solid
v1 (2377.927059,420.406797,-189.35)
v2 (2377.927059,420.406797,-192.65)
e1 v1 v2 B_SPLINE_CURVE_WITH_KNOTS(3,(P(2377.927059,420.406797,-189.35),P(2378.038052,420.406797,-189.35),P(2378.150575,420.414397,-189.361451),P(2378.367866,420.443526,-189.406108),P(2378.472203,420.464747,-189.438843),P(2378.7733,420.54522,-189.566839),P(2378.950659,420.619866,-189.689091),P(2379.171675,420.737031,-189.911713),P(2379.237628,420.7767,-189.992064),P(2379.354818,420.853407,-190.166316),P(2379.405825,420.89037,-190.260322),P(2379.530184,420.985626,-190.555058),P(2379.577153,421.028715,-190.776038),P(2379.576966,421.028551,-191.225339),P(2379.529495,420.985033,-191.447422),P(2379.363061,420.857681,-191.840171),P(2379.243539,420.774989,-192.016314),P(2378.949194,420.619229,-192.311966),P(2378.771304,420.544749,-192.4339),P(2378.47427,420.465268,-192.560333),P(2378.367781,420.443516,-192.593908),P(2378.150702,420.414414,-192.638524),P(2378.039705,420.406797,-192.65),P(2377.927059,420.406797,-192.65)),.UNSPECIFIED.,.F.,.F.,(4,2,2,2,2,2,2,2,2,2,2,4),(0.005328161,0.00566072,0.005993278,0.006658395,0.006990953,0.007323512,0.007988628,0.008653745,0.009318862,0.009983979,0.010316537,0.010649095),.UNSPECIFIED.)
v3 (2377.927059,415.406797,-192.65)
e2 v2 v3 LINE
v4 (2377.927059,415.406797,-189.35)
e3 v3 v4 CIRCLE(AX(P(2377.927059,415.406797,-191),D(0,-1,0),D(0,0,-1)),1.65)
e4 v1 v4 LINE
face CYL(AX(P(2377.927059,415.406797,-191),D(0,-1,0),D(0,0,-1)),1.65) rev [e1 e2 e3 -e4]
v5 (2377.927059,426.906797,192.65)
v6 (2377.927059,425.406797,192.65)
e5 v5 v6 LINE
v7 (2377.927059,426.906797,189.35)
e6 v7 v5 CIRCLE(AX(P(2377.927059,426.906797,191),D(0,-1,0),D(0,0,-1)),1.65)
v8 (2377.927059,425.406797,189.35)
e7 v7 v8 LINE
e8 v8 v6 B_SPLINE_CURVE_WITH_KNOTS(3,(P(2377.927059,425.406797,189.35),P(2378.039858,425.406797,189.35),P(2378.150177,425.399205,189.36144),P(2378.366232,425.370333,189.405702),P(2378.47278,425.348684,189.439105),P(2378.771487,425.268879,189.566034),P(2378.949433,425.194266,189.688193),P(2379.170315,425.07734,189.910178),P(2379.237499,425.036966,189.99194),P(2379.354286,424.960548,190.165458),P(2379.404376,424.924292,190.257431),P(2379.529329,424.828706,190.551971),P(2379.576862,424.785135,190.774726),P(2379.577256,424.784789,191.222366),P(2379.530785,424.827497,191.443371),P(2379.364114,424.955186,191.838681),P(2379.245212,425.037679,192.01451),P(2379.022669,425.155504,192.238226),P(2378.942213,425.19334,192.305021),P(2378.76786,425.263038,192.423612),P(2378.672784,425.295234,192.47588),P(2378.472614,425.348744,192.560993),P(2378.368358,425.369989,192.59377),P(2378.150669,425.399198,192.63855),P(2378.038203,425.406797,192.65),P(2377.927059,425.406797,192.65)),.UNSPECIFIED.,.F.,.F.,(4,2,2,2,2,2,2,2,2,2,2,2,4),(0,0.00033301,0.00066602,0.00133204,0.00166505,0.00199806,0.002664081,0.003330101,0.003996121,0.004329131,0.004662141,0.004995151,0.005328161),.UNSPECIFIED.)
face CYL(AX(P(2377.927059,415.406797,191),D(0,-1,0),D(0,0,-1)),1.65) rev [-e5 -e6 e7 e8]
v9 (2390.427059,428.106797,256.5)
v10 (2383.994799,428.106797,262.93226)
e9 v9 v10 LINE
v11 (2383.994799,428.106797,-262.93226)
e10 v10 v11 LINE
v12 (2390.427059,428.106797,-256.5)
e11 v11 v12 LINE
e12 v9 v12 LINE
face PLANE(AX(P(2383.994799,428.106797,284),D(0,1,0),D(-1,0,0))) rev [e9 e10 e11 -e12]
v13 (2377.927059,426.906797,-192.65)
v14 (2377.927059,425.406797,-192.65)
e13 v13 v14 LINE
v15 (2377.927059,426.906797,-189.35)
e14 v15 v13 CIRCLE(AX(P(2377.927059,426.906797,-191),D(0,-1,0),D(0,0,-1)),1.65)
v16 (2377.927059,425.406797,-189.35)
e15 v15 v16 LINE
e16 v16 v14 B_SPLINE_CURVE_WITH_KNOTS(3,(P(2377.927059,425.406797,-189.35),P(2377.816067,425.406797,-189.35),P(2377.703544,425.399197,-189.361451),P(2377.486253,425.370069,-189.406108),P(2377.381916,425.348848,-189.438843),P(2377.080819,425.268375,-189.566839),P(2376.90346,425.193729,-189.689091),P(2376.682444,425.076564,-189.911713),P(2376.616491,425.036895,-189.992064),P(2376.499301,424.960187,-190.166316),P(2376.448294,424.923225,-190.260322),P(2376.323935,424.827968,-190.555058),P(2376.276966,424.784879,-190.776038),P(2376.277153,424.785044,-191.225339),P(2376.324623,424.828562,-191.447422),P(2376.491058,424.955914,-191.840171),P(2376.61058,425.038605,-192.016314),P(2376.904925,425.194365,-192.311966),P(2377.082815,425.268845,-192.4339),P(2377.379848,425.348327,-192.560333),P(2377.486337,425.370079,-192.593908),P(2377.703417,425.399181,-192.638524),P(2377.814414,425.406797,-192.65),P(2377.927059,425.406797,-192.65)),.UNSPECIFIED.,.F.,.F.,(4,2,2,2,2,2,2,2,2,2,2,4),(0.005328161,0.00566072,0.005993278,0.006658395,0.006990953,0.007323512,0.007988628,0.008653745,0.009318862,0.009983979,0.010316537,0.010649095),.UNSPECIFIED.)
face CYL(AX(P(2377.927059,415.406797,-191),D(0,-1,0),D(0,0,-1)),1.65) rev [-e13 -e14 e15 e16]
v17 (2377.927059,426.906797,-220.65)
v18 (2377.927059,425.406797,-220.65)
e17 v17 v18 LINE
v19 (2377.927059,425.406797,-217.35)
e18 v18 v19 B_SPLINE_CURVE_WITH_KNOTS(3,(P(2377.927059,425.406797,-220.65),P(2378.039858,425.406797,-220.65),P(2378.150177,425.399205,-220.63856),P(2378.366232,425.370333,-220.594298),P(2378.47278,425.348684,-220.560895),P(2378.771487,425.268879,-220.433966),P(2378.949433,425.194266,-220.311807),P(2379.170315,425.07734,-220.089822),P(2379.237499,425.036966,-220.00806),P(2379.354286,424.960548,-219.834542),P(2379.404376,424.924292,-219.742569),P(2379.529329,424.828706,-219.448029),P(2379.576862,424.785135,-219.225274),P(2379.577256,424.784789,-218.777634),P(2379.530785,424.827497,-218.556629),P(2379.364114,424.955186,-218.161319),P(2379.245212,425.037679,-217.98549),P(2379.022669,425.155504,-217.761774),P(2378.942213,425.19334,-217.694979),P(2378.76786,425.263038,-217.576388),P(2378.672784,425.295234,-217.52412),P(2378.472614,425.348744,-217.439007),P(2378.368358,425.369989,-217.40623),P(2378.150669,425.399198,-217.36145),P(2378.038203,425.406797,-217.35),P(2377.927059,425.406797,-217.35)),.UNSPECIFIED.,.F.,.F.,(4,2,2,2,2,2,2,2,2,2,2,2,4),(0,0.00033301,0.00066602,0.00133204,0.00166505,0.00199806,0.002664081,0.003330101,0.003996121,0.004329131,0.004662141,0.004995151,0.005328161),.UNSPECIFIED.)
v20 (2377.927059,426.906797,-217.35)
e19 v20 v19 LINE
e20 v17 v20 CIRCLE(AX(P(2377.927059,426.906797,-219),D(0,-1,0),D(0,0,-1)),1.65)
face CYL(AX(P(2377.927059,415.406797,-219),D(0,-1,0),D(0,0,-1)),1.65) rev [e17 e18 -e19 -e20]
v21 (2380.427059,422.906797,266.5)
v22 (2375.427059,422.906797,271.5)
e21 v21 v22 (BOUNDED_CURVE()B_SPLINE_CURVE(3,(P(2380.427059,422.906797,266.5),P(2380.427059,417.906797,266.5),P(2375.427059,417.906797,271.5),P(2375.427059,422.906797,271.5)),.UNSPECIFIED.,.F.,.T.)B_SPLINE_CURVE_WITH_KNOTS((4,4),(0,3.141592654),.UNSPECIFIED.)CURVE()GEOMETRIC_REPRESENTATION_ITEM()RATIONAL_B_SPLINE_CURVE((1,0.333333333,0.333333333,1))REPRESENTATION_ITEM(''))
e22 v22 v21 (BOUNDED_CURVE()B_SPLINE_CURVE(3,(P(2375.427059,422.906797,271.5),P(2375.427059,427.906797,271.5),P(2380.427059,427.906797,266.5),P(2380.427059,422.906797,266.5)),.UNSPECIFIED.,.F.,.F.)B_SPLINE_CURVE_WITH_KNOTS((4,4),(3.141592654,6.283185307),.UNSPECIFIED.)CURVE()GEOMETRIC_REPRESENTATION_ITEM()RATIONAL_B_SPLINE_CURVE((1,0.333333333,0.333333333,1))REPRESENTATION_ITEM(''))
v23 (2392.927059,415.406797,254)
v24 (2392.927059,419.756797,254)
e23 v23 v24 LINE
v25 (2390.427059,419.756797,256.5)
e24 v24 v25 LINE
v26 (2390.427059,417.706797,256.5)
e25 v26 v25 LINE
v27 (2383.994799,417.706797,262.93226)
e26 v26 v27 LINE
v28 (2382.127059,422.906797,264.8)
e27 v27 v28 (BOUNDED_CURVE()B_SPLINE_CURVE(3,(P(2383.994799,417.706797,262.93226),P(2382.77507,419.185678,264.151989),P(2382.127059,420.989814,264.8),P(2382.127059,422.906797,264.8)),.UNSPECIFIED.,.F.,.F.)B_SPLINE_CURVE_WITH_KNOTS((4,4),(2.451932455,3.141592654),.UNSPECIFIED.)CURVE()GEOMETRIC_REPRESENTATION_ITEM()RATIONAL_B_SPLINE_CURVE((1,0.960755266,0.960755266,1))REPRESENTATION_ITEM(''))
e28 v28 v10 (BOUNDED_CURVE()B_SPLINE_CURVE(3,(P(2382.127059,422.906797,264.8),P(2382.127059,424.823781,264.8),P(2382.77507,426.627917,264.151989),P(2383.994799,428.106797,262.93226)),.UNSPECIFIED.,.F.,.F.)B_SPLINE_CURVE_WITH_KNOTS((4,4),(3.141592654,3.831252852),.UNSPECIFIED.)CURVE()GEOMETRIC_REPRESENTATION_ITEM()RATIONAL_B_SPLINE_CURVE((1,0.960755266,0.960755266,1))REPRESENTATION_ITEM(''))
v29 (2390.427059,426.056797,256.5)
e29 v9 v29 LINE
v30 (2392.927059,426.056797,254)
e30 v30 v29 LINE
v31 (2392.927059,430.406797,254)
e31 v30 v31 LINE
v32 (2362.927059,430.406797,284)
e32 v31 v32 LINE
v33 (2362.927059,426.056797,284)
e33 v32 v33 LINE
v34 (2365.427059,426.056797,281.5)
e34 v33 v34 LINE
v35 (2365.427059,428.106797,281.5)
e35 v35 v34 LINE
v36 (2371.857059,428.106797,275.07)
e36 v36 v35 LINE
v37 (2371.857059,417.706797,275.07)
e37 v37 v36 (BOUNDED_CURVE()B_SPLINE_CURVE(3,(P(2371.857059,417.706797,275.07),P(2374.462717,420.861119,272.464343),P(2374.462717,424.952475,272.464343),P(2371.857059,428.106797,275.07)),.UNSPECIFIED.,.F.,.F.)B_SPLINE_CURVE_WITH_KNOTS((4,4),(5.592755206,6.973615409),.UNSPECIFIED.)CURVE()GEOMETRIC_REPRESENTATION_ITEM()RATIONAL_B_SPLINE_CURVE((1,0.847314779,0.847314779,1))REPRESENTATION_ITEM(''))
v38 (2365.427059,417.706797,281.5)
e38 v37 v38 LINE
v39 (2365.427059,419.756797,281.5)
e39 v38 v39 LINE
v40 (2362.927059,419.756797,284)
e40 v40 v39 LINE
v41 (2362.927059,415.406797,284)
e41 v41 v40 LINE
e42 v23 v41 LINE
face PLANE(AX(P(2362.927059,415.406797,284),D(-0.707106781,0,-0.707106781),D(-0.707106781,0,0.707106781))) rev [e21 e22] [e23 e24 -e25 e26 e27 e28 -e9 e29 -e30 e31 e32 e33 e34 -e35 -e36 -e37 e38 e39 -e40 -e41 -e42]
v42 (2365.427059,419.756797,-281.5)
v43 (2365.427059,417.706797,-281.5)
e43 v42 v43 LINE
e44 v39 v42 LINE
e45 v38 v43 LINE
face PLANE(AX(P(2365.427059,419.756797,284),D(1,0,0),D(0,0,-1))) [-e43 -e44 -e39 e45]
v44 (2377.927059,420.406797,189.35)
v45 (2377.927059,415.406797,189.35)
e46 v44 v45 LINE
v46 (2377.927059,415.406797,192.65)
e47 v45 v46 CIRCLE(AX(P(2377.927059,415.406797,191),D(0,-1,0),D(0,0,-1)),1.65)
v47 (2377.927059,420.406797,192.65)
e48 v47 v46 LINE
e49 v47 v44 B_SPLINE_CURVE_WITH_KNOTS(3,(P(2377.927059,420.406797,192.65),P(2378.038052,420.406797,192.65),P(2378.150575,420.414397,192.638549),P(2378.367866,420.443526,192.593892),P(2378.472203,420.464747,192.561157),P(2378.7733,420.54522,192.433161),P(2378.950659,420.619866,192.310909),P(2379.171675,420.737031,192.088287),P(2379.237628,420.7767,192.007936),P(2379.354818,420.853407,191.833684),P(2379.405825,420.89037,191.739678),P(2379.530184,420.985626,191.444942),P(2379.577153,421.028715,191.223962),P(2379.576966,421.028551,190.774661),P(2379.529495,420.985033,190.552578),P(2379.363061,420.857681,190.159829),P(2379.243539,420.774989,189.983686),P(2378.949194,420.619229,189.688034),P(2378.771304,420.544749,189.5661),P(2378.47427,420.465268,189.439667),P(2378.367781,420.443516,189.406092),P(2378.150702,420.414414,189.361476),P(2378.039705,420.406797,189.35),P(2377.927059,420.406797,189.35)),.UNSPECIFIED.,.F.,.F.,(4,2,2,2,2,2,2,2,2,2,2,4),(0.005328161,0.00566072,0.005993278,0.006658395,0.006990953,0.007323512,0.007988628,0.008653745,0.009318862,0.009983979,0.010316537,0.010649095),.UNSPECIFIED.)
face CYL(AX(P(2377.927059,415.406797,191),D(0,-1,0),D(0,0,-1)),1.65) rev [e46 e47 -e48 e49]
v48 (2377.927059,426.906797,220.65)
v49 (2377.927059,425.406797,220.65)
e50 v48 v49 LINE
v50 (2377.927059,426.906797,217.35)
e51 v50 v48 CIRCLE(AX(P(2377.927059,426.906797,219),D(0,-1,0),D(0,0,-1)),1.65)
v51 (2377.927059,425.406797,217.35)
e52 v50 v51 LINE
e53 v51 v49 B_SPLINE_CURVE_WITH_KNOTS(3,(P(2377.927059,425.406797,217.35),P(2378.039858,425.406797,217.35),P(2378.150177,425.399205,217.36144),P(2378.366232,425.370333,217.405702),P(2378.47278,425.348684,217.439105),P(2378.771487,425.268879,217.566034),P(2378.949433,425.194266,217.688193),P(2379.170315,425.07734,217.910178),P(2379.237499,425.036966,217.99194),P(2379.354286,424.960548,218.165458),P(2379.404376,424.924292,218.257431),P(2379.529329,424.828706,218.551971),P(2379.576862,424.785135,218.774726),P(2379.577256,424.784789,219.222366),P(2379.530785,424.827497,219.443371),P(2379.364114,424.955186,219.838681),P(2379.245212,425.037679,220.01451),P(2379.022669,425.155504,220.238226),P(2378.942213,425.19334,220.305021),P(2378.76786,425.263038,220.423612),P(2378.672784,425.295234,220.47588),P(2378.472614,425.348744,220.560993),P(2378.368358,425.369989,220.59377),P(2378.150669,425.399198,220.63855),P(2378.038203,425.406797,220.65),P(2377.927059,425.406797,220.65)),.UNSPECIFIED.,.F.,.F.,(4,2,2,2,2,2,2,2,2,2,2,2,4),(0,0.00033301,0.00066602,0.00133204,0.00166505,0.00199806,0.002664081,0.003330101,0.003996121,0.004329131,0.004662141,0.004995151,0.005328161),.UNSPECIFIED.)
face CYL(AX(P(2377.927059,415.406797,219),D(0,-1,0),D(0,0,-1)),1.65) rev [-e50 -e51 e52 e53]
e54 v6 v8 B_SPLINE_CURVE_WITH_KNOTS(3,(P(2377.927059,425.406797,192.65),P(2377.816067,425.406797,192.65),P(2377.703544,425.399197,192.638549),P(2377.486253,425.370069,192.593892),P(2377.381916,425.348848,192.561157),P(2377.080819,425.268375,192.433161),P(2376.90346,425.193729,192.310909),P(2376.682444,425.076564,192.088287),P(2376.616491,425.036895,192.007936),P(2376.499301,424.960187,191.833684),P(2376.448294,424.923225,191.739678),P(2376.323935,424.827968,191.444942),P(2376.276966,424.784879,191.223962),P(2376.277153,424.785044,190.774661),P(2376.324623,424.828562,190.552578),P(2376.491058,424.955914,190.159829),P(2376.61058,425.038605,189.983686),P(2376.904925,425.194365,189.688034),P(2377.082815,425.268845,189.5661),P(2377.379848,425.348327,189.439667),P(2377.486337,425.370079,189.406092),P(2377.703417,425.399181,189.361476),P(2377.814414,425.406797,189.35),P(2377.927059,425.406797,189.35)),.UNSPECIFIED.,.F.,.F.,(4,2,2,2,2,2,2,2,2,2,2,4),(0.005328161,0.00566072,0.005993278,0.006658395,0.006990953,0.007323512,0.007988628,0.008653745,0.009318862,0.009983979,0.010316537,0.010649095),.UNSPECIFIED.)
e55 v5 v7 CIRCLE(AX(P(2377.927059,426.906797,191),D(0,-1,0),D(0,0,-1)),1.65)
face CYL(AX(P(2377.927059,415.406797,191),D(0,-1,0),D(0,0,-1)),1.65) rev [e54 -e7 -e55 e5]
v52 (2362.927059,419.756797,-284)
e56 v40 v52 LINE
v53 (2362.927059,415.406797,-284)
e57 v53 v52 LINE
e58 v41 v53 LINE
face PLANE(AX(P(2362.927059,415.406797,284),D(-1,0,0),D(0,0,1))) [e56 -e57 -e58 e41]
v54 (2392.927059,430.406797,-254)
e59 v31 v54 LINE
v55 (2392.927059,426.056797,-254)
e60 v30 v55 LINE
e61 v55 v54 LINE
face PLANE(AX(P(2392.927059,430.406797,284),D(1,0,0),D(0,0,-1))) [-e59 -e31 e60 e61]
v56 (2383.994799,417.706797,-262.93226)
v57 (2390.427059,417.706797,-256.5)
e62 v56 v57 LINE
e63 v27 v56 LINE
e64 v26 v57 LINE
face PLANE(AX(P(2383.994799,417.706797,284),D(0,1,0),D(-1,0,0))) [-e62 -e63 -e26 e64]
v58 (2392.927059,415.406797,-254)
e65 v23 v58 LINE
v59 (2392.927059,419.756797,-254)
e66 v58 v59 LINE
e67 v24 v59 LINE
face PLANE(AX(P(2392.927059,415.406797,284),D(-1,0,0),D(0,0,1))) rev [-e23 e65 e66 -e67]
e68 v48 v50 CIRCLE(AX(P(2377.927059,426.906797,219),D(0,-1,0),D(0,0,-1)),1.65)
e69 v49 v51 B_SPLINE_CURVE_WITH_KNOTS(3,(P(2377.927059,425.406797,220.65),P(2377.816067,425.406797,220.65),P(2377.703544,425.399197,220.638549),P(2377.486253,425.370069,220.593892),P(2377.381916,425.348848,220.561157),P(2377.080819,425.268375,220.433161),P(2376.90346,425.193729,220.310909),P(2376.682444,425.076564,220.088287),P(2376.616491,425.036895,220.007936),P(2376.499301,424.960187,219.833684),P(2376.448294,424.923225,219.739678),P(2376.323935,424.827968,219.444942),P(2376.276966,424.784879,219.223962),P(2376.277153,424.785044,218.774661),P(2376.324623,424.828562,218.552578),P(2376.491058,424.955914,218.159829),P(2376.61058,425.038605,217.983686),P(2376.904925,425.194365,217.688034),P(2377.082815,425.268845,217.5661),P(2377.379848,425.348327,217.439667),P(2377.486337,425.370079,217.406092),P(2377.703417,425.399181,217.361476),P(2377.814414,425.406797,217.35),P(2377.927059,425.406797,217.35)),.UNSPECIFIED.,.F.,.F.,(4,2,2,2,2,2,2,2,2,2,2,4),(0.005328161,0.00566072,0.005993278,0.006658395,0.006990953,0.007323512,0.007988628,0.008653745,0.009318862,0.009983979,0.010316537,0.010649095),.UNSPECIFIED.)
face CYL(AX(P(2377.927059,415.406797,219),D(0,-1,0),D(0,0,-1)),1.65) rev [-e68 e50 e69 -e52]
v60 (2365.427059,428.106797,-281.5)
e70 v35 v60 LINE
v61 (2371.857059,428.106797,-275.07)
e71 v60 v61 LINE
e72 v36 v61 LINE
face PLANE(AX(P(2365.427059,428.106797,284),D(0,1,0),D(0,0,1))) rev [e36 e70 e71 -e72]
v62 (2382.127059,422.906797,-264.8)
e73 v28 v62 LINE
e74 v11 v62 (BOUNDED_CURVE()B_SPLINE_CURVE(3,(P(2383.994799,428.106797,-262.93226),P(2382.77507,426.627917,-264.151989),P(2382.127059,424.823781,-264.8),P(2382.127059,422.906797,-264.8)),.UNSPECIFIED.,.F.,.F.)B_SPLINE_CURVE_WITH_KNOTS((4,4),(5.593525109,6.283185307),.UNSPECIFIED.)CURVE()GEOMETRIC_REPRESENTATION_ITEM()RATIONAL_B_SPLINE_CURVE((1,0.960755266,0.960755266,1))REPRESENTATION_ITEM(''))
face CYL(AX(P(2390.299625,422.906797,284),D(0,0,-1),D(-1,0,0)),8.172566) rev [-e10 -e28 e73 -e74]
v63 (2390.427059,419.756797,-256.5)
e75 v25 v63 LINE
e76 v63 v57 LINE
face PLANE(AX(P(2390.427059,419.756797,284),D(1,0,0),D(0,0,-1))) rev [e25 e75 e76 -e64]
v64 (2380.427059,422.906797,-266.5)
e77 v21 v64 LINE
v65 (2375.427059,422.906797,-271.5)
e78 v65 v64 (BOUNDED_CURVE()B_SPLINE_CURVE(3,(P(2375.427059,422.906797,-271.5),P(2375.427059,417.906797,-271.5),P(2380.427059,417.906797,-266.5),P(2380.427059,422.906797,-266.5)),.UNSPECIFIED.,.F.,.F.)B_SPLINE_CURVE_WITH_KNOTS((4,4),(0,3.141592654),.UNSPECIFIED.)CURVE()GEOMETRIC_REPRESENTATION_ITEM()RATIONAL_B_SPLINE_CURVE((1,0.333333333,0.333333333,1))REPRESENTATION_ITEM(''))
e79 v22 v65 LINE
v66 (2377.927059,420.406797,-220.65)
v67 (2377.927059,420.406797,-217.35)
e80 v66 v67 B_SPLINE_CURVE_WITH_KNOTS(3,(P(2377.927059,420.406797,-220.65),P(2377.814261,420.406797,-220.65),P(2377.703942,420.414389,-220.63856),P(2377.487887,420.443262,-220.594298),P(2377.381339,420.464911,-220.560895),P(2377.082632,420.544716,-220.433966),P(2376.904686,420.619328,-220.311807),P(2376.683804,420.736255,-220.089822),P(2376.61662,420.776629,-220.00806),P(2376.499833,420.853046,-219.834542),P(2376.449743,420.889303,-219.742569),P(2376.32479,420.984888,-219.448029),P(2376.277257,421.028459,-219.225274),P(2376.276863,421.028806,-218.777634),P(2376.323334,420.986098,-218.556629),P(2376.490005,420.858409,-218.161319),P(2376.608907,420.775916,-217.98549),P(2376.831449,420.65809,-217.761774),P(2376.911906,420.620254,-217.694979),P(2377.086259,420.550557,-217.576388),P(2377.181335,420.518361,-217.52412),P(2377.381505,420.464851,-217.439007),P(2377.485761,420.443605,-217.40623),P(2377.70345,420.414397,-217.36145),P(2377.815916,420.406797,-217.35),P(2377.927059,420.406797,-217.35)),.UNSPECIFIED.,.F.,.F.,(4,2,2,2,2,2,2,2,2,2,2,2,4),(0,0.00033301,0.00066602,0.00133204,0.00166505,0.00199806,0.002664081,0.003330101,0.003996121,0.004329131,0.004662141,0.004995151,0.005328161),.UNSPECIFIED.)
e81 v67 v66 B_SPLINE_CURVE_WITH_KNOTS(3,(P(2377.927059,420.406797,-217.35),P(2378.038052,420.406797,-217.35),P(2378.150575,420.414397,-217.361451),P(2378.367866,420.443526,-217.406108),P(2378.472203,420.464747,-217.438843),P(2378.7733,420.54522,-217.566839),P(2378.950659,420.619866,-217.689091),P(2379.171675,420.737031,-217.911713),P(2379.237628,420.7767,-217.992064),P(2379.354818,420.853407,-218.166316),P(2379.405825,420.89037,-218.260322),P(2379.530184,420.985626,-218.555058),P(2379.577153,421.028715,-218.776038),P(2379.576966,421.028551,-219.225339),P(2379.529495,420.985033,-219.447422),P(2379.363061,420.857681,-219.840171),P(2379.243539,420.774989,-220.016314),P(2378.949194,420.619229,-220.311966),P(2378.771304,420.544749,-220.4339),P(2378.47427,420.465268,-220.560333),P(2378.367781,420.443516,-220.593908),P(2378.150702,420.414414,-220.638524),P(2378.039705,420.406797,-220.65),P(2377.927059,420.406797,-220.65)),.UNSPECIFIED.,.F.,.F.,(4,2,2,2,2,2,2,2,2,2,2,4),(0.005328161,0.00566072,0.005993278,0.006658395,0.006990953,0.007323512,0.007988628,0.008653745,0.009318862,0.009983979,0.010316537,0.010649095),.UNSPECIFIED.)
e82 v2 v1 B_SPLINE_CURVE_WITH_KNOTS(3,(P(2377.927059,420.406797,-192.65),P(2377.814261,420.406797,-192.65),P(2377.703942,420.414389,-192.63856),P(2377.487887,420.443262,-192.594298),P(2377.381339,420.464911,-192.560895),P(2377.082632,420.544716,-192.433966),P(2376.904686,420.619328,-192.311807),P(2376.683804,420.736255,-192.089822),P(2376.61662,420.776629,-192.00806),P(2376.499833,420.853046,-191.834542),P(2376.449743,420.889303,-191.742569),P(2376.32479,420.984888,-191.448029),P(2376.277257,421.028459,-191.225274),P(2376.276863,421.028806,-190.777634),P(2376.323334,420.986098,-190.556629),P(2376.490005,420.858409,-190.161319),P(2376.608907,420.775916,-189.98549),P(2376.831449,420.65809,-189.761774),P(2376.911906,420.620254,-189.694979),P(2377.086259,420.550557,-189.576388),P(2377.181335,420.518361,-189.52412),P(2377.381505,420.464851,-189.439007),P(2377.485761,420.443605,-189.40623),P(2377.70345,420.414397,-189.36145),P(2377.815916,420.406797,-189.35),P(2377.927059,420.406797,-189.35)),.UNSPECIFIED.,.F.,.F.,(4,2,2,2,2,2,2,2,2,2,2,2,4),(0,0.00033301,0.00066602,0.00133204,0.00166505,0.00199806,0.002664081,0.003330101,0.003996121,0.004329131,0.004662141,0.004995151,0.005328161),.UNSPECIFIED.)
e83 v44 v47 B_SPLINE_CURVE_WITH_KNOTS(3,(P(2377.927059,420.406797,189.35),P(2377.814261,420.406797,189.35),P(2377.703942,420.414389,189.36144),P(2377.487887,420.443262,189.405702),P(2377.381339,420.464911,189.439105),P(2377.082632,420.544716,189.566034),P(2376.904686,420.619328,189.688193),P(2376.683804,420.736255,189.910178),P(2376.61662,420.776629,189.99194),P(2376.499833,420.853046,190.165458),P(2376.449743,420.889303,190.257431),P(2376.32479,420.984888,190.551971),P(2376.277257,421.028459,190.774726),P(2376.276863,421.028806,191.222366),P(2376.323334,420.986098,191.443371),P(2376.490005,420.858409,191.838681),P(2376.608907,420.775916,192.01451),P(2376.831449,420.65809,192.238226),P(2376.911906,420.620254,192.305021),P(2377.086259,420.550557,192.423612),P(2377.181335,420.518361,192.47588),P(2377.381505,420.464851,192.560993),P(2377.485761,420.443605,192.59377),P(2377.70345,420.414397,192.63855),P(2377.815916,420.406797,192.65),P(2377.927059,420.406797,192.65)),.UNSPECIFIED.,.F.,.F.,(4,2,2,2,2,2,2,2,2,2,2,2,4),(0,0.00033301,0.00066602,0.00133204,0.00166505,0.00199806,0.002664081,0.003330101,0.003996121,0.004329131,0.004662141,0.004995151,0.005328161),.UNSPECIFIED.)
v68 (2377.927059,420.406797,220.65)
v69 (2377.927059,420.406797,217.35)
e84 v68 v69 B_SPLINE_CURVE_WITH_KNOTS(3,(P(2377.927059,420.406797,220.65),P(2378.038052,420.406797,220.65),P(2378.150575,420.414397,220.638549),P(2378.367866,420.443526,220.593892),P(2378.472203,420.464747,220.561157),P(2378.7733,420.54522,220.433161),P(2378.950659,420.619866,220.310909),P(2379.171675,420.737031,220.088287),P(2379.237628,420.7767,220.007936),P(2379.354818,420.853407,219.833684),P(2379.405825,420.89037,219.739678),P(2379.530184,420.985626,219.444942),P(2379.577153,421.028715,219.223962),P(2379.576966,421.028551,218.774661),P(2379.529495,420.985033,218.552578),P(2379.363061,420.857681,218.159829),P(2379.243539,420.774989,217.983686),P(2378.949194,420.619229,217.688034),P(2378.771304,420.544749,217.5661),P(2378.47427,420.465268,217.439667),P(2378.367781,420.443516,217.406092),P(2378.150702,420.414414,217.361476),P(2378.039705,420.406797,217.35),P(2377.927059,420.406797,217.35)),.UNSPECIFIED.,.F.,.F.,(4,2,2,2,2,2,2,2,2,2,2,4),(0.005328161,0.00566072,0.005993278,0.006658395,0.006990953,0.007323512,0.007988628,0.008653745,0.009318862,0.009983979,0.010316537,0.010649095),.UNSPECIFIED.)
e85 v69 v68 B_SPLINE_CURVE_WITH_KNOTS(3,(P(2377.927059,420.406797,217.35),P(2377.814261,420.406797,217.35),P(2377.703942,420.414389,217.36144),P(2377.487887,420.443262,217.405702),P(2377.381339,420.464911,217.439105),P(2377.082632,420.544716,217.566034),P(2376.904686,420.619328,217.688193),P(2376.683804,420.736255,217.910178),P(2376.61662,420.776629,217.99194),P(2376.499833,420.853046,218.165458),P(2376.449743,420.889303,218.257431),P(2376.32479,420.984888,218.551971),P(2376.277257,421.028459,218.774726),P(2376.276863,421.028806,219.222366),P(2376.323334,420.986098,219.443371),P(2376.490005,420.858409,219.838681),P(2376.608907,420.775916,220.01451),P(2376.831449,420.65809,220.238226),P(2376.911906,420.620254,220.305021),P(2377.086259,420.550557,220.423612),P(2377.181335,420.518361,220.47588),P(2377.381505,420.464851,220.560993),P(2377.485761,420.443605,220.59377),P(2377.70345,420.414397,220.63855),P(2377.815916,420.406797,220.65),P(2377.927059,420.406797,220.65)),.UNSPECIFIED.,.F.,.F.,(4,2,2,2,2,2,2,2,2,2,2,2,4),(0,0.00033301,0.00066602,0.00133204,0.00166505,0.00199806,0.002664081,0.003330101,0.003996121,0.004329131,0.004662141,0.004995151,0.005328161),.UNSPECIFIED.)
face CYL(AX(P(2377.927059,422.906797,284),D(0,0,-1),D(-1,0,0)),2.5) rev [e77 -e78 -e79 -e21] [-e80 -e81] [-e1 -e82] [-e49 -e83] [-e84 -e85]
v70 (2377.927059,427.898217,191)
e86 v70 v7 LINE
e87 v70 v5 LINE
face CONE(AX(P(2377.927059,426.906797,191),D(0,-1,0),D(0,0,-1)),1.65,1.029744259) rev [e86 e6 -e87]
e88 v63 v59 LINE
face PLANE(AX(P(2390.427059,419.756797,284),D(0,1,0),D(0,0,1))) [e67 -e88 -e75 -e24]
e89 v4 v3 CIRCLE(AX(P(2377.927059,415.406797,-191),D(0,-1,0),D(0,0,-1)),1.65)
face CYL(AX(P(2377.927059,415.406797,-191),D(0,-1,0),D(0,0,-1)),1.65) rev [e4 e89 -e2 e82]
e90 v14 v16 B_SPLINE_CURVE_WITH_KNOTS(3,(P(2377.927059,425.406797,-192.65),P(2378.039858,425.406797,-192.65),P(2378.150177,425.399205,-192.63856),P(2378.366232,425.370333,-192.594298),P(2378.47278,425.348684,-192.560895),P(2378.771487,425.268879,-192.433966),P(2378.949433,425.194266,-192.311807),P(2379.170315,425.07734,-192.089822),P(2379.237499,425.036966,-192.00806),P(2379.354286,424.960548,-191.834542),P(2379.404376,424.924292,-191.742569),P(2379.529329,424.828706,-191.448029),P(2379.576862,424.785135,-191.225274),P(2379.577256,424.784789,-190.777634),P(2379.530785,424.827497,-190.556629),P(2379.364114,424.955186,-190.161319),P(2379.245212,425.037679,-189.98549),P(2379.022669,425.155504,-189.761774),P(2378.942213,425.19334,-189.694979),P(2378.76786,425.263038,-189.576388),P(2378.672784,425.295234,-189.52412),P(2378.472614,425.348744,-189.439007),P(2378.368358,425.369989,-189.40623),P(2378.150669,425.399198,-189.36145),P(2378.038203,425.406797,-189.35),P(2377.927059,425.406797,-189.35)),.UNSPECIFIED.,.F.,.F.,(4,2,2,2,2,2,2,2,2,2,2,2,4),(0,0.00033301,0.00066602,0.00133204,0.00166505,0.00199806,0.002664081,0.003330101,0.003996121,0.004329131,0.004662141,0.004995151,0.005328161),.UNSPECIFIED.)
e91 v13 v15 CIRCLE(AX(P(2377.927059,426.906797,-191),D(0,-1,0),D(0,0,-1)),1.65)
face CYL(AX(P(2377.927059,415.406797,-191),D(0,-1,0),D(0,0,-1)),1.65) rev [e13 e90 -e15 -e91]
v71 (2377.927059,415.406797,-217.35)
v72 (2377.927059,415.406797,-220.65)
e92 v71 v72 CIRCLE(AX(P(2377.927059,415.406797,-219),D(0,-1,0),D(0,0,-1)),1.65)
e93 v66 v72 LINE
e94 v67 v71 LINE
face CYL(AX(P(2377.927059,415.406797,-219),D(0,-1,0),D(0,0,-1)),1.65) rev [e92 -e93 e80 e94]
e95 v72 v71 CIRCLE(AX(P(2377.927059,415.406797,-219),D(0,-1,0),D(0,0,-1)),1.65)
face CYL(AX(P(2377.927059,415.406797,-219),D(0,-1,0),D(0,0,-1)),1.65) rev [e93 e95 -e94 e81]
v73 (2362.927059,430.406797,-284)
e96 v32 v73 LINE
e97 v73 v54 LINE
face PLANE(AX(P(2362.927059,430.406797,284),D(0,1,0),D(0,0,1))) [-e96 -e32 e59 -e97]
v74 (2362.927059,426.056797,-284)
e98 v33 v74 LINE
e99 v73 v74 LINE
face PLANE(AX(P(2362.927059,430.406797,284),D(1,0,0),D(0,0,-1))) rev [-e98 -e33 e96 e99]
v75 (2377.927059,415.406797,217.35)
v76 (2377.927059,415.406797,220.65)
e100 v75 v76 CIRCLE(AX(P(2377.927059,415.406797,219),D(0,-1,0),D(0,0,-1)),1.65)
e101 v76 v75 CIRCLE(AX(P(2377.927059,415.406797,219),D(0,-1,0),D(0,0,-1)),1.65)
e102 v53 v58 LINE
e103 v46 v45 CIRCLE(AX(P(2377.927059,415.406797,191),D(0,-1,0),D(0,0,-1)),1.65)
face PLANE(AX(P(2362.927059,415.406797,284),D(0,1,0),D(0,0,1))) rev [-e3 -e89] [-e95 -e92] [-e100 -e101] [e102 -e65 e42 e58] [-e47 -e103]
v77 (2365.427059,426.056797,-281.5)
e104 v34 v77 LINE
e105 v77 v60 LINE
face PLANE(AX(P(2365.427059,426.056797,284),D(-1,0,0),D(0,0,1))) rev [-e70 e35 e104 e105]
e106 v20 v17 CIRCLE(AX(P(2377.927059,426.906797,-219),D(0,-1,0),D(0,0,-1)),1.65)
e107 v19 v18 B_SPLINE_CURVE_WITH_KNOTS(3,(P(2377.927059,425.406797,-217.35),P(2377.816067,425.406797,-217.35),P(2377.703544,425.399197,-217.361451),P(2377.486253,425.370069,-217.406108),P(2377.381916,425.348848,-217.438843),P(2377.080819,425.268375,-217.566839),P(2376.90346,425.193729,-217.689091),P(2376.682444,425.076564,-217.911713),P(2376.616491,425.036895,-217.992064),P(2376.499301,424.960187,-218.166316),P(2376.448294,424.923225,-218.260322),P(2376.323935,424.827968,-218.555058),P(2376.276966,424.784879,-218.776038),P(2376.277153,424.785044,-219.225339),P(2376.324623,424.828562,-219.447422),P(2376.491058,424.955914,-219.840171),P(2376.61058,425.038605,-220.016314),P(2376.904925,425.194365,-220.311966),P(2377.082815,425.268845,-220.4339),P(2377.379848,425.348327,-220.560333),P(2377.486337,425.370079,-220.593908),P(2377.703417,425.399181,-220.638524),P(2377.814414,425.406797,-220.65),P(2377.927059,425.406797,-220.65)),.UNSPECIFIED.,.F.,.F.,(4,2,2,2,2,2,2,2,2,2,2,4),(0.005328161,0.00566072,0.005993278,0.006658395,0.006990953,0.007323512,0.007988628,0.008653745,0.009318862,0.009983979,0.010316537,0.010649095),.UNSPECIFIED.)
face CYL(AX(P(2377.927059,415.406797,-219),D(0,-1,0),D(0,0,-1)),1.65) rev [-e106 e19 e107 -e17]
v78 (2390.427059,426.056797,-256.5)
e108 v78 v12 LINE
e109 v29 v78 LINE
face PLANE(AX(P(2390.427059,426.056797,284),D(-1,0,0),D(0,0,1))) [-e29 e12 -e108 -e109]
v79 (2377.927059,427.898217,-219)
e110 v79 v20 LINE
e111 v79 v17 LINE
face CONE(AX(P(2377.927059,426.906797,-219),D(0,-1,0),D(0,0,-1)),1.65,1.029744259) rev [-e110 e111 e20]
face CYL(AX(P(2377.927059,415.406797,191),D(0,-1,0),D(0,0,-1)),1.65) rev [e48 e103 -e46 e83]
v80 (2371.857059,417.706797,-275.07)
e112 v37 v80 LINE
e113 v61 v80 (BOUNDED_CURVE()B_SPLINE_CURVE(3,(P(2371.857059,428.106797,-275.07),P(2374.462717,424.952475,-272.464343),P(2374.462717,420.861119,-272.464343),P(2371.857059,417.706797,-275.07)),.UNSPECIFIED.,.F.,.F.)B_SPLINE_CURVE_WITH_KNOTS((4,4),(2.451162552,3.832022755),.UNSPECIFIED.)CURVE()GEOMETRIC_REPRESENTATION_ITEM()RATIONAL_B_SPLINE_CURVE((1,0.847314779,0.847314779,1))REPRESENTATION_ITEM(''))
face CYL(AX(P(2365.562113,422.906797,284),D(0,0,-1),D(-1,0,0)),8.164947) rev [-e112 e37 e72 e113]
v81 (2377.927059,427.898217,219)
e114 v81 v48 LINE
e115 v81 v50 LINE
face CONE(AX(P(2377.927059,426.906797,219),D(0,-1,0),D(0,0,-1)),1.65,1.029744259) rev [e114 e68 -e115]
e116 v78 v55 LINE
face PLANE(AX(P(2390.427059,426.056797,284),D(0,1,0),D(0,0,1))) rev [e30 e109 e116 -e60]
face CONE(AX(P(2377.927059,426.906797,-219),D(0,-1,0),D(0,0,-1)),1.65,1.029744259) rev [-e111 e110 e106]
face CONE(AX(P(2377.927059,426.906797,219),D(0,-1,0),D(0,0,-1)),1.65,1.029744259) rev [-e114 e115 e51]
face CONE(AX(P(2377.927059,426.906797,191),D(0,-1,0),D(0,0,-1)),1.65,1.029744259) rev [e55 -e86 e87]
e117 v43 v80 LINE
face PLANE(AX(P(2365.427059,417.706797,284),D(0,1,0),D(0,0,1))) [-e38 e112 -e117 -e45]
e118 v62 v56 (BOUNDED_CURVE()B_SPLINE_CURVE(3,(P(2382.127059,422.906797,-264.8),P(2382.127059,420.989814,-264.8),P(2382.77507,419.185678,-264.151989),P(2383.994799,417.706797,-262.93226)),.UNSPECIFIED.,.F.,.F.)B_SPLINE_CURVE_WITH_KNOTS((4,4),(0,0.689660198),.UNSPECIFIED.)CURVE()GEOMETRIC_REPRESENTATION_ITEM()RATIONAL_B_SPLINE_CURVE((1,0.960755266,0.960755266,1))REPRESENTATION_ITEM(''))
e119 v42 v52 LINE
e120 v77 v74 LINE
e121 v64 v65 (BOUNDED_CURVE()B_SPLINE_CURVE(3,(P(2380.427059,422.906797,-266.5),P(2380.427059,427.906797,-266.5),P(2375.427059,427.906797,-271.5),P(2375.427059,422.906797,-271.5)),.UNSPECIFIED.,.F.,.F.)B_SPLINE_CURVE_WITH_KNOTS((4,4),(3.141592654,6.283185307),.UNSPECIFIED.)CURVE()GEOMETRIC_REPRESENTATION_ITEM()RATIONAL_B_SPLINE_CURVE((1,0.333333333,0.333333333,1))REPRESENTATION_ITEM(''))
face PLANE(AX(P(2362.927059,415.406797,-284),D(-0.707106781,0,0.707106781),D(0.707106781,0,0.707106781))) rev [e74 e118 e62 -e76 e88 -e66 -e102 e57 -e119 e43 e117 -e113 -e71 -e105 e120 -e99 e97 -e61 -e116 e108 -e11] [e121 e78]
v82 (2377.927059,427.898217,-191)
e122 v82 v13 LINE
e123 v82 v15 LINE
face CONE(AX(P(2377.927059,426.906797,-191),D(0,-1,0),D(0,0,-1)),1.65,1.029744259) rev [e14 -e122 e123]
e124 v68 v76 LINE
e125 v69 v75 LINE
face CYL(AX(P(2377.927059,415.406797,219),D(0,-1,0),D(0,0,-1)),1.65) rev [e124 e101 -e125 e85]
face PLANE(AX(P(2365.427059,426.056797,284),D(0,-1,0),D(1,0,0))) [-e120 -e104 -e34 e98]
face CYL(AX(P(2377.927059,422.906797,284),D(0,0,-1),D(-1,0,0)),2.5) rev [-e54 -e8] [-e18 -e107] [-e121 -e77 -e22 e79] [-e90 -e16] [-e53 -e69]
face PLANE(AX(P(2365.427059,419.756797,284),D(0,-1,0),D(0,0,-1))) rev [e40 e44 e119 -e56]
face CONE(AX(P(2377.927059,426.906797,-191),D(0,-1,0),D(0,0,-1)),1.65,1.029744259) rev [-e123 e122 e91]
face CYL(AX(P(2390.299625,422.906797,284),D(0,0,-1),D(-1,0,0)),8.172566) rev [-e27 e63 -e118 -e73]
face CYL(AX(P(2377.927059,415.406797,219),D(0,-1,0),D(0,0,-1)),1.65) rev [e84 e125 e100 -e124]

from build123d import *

# Parameters (mm, degrees)
MODEL_R                = 2.5
EXTRUDE_1_DEPTH        = 284
CUT_EXTRUDE_1_DEPTH    = 2410.767812852
HOLE_WIZARD_M4_1_D     = 3.3
HOLE_WIZARD_M4_1_DEPTH = 11.5
HOLE_WIZARD_M4_1_TIP   = 0.991420021


with BuildPart() as part:
    # Model → 凸台-拉伸1 (new, symmetric)
    with BuildSketch(Plane.XY):
        with BuildLine():
            Line((2390.427059452, 419.756797217), (2392.927059452, 419.756797217))
            Line((2392.927059452, 419.756797217), (2392.927059452, 415.406797217))
            Line((2392.927059452, 415.406797217), (2362.927059452, 415.406797217))
            Line((2362.927059452, 415.406797217), (2362.927059452, 419.756797217))
            Line((2362.927059452, 419.756797217), (2365.427059452, 419.756797217))
            Line((2365.427059452, 419.756797217), (2365.427059452, 417.706797217))
            Line((2365.427059452, 417.706797217), (2371.857059452, 417.706797217))
            ThreePointArc((2371.857059452, 417.706797217), (2373.727059452, 422.906797217), (2371.857059452, 428.106797217))
            Line((2371.857059452, 428.106797217), (2365.427059452, 428.106797217))
            Line((2365.427059452, 428.106797217), (2365.427059452, 426.056797217))
            Line((2365.427059452, 426.056797217), (2362.927059452, 426.056797217))
            Line((2362.927059452, 426.056797217), (2362.927059452, 430.406797217))
            Line((2362.927059452, 430.406797217), (2392.927059452, 430.406797217))
            Line((2392.927059452, 430.406797217), (2392.927059452, 426.056797217))
            Line((2392.927059452, 426.056797217), (2390.427059452, 426.056797217))
            Line((2390.427059452, 426.056797217), (2390.427059452, 428.106797217))
            Line((2390.427059452, 428.106797217), (2383.994799144, 428.106797217))
            ThreePointArc((2383.994799144, 428.106797217), (2382.127059452, 422.906797217), (2383.994799144, 417.706797217))
            Line((2383.994799144, 417.706797217), (2390.427059452, 417.706797217))
            Line((2390.427059452, 417.706797217), (2390.427059452, 419.756797217))
        make_face()
        with Locations((2377.927059452, 422.906797217)):
            Circle(MODEL_R, mode=Mode.SUBTRACT)
    extrude(amount=EXTRUDE_1_DEPTH, both=True)

    # 草图1 → 切除-拉伸1 (cut, through all)
    with BuildSketch(Plane(origin=(0, 430.406797217, 0), x_dir=(1, 0, 0), z_dir=(0, 1, 0))):
        Polygon((2362.927059452, 284), (2392.927059452, 254), (2392.927059452, 284), align=None)
        Polygon((2362.927059452, -284), (2392.927059452, -254), (2392.927059452, -284), align=None)
    extrude(amount=-CUT_EXTRUDE_1_DEPTH, mode=Mode.SUBTRACT)

    # M4 螺纹孔1
    with Locations(Plane(origin=(0, 415.406797217, 0), x_dir=(-1, 0, 0), z_dir=(0, -1, 0))):
        with Locations((-2377.927059452, -219), (-2377.927059452, -191), (-2377.927059452, 191), (-2377.927059452, 219)):
            Hole(HOLE_WIZARD_M4_1_D / 2, depth=HOLE_WIZARD_M4_1_DEPTH)
            with Locations((0, 0, -(HOLE_WIZARD_M4_1_DEPTH + HOLE_WIZARD_M4_1_TIP / 2))):  # 118° drill point
                Cone(0, HOLE_WIZARD_M4_1_D / 2, HOLE_WIZARD_M4_1_TIP, mode=Mode.SUBTRACT)


solid = part.part
